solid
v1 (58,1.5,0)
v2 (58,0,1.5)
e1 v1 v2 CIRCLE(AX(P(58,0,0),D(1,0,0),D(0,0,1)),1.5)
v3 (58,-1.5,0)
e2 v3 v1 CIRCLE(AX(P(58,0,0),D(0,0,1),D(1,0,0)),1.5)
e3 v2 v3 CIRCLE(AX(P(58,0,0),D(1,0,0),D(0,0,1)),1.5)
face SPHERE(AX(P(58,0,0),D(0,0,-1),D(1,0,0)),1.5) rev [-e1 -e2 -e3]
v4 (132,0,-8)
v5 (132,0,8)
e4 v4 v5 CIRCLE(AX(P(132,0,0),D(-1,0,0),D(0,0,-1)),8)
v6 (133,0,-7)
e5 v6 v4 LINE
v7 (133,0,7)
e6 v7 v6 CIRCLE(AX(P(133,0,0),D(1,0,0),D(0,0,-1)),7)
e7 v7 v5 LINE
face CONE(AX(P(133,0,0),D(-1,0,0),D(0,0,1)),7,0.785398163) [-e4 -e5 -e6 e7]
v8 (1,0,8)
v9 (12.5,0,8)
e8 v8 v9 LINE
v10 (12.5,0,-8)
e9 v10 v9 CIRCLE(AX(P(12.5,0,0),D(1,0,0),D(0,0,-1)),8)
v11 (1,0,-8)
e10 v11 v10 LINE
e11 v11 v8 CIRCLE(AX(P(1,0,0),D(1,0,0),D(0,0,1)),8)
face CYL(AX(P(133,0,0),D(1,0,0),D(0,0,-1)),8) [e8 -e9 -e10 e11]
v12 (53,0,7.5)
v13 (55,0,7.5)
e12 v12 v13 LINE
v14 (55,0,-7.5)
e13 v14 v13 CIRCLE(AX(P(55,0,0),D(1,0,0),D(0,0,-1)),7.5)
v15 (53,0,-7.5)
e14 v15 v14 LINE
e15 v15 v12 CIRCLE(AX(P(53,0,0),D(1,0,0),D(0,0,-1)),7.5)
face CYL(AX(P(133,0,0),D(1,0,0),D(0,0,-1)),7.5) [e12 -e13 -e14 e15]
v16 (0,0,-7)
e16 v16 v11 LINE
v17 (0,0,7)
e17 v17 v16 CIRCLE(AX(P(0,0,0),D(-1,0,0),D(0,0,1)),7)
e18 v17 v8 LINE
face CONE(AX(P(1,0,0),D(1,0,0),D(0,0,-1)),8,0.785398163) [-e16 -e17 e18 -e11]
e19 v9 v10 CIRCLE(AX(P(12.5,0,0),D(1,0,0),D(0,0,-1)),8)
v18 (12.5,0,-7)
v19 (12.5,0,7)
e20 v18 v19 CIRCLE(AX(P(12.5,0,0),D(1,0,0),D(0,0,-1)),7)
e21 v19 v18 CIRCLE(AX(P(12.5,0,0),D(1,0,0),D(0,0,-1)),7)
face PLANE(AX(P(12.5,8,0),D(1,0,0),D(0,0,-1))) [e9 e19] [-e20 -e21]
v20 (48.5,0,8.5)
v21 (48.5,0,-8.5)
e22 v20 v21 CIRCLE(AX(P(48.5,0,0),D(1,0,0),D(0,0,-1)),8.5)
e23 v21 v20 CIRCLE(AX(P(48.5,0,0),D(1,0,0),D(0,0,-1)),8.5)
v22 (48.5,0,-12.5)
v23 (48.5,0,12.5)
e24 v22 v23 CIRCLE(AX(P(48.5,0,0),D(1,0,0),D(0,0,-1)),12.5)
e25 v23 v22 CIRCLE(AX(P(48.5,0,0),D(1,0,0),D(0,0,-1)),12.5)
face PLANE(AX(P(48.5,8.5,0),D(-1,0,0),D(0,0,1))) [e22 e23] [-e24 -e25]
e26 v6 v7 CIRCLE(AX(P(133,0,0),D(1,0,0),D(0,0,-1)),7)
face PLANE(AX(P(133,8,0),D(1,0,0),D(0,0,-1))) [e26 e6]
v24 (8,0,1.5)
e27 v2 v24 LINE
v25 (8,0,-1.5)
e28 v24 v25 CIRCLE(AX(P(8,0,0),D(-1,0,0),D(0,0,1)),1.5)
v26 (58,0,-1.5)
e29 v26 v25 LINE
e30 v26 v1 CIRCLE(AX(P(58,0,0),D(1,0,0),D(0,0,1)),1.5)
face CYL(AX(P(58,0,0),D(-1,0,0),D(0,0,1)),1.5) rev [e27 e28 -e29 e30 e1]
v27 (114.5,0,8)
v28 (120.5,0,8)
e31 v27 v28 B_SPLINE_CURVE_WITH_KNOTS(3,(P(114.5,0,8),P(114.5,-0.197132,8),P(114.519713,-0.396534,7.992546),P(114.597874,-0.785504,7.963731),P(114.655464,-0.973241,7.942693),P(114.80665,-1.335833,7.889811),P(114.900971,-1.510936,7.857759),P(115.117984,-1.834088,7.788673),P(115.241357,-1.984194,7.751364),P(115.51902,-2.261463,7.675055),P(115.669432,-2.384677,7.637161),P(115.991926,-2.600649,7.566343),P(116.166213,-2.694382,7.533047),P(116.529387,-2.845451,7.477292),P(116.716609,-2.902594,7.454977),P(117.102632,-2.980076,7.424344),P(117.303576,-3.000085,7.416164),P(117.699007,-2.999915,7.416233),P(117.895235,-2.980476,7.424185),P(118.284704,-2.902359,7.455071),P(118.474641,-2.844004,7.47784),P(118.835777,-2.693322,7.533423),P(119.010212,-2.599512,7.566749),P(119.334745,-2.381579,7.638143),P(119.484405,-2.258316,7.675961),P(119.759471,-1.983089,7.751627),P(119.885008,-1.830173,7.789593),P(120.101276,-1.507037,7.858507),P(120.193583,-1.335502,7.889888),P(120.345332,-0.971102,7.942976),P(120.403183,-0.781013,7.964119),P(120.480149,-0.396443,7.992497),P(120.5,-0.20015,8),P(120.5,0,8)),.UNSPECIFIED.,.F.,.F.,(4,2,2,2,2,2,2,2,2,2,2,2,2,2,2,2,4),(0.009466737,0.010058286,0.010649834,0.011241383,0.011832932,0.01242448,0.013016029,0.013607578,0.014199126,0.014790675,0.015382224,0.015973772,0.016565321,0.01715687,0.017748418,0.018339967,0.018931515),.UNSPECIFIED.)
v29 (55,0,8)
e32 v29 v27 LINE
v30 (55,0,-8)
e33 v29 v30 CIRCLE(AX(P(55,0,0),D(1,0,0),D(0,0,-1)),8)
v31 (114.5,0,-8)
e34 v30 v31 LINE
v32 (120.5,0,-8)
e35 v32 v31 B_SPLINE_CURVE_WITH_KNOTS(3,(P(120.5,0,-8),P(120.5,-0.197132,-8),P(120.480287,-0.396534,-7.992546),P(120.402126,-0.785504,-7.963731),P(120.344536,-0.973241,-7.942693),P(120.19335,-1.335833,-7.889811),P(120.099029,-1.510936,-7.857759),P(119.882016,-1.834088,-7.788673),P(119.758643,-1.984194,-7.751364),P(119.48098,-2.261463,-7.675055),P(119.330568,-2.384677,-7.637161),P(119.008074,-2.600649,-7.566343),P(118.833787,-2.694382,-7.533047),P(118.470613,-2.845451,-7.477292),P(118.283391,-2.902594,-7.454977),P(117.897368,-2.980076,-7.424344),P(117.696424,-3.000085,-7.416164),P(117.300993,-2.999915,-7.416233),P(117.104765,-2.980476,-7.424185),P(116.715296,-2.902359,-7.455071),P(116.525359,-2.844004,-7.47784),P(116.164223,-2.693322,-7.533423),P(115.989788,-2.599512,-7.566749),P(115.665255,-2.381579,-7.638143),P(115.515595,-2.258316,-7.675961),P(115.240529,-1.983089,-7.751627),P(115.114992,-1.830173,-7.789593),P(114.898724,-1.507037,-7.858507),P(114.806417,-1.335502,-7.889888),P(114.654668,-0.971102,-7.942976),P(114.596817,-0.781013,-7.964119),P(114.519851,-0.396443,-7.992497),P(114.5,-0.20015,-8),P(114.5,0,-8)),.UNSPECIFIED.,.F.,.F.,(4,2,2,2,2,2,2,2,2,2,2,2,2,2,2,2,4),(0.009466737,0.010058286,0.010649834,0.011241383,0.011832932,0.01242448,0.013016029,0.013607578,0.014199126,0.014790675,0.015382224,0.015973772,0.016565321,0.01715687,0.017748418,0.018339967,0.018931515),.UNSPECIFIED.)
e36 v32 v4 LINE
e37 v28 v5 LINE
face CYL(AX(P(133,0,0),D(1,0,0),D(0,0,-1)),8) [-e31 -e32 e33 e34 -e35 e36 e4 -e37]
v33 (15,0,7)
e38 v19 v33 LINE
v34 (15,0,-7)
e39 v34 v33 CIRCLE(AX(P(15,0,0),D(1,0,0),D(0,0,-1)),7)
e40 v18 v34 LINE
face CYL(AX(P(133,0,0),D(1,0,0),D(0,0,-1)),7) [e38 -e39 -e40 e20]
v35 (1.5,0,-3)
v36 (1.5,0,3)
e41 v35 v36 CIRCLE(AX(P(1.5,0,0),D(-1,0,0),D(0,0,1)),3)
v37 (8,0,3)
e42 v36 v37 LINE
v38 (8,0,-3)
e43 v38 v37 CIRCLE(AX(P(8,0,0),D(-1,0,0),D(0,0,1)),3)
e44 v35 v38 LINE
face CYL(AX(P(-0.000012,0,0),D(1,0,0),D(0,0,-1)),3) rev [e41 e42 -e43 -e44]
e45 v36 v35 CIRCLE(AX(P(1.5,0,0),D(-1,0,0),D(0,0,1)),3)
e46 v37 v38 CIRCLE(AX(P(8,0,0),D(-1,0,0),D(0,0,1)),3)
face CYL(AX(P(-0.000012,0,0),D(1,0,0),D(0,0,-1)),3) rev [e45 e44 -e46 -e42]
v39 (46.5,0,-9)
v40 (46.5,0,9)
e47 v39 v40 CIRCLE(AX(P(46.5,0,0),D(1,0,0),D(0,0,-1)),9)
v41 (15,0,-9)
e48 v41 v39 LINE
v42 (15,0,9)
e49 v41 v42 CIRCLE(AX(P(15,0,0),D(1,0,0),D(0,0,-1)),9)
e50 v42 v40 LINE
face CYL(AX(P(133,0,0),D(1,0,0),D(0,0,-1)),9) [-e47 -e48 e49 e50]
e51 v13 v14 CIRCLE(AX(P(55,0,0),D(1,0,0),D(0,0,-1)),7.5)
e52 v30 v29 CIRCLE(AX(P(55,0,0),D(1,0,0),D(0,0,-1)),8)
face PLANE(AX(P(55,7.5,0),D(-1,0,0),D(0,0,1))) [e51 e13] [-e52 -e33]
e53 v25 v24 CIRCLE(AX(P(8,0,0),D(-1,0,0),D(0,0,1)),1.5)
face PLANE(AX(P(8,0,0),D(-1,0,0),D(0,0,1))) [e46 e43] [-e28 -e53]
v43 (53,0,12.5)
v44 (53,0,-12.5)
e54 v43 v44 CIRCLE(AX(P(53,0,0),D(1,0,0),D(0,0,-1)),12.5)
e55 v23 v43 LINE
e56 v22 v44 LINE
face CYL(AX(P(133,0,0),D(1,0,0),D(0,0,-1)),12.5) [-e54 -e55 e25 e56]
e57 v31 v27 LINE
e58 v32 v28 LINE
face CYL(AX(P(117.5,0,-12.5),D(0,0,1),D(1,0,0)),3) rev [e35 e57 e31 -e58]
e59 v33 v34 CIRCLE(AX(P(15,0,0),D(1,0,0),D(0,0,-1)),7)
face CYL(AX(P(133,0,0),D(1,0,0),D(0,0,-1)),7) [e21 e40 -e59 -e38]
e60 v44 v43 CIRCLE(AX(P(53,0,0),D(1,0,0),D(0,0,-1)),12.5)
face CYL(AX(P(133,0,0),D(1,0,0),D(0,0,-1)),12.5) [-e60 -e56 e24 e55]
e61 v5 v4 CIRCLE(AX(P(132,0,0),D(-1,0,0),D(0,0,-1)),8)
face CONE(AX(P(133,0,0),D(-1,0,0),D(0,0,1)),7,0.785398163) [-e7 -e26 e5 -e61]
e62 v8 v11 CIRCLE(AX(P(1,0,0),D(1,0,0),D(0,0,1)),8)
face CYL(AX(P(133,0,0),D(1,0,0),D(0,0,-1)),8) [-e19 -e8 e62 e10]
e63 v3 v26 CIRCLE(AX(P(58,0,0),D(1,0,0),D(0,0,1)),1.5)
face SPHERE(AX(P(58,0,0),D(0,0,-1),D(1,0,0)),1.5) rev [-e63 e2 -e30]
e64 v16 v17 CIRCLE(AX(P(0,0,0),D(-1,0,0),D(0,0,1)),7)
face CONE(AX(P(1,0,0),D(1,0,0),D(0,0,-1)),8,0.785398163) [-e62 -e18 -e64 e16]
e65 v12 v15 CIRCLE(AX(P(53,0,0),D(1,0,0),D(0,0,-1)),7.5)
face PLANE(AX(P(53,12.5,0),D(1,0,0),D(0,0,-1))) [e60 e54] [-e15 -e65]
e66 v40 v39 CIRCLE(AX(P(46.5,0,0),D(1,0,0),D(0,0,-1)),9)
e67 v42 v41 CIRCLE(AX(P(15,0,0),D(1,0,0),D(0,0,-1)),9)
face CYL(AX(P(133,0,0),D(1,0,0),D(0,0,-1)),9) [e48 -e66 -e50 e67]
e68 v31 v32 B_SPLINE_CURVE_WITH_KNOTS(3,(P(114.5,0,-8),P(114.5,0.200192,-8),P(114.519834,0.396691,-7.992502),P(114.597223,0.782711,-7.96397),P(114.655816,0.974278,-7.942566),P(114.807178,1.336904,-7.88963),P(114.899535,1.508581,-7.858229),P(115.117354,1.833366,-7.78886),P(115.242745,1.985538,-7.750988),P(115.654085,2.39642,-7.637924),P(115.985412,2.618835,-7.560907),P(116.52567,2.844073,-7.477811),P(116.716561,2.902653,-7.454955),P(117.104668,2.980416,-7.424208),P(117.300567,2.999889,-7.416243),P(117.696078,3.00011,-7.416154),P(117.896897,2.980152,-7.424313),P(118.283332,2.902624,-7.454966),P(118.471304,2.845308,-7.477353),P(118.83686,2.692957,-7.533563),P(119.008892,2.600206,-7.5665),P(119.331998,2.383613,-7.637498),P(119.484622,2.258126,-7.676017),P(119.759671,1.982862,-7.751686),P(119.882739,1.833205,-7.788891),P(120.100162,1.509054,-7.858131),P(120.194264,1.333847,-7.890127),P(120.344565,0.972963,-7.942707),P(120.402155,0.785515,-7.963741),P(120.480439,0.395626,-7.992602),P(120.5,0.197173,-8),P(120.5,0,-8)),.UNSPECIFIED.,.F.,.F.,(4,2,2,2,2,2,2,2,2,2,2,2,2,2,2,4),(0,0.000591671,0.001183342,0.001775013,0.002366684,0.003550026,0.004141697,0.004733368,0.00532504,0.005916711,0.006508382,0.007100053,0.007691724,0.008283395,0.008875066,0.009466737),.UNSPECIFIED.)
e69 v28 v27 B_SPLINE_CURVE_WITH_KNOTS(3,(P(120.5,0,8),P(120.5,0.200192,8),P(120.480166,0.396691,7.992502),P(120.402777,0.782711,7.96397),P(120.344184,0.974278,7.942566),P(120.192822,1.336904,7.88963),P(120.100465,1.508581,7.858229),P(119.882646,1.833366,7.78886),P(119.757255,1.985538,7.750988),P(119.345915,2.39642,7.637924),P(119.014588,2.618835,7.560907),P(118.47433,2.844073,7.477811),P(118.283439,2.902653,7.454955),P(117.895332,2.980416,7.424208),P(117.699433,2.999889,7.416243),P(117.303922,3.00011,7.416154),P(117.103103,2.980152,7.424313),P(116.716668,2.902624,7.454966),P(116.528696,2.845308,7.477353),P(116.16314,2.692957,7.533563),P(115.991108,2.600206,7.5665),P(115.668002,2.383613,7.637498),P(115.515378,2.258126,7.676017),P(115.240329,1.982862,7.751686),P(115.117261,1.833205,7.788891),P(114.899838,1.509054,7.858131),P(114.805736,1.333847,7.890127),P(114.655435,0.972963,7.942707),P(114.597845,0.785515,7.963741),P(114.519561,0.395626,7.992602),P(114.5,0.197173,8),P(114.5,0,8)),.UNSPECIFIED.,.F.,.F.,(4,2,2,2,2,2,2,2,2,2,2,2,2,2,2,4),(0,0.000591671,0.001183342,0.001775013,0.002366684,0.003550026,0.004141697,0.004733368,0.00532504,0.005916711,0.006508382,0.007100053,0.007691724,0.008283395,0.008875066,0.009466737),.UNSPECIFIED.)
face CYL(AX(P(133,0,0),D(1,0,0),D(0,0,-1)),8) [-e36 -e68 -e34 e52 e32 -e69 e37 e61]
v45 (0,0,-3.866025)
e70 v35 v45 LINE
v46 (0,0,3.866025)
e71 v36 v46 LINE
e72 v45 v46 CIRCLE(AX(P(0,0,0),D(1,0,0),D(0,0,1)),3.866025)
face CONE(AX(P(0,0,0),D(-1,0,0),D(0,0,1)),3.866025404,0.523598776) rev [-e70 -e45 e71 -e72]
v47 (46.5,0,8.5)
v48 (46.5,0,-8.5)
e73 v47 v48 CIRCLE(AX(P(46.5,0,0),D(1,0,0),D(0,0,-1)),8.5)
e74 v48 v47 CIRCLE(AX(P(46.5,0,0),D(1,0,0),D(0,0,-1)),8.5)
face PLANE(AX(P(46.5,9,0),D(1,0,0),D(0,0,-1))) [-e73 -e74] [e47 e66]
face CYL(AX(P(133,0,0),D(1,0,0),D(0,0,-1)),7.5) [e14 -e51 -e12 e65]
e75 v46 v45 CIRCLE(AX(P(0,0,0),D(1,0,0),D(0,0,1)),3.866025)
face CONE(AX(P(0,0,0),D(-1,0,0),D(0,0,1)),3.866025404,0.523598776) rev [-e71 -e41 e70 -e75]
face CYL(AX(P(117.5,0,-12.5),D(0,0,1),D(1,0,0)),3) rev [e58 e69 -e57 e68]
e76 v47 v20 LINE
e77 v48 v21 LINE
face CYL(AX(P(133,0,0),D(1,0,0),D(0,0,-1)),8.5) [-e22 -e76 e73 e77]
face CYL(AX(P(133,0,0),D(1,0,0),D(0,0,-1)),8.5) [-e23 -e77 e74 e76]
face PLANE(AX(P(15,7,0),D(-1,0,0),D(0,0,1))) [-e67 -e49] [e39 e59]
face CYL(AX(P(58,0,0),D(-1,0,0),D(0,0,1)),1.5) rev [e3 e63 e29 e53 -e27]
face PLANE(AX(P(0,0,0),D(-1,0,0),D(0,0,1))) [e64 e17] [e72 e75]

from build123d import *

# Parameters (mm, degrees)
CUT_EXTRUDE1_DEPTH      = 135.169668703
CUT_EXTRUDE1_DEPTH_BACK = 135.169668703
SKETCH2_R               = 3
CUT_EXTRUDE2_DEPTH      = 135.169668803
CUT_EXTRUDE2_DEPTH_BACK = 8
SKETCH3_R               = 3
SKETCH4_R               = 1.5
CUT_EXTRUDE3_DEPTH      = 50
CHAMFER1_SIZE           = 1.5
CHAMFER1_SIZE2          = 0.866025404
CHAMFER2_SIZE           = 1


with BuildPart() as part:
    # Sketch1 → Revolve1 (revolve)
    with BuildSketch(Plane.XY, mode=Mode.PRIVATE) as revolve1_sk:
        Polygon((0, 0), (0, 8), (12.5, 8), (12.5, 7), (15, 7), (15, 9), (46.5, 9), (46.5, 8.5), (48.5, 8.5), (48.5, 12.5), (53, 12.5), (53, 7.5), (55, 7.5), (55, 8), (133, 8), (133, 0), align=None)
    revolve(revolve1_sk.sketch.rotate(Axis((133, 0, 0), (-1, 0, 0)), 90), axis=Axis((133, 0, 0), (-1, 0, 0)))

    # Sketch2 → Cut-Extrude1 (cut, two sides: drawn at the far end of the back side and taken through both)
    with BuildSketch(Plane.XY.offset(-CUT_EXTRUDE1_DEPTH_BACK)):
        with Locations((117.5, 0)):
            Circle(SKETCH2_R)
    extrude(amount=CUT_EXTRUDE1_DEPTH + CUT_EXTRUDE1_DEPTH_BACK, mode=Mode.SUBTRACT)

    # Sketch3 → Cut-Extrude2 (cut, two sides: drawn at the far end of the back side and taken through both)
    with BuildSketch(Plane.ZY.offset(-CUT_EXTRUDE2_DEPTH_BACK)):
        with Locations(Location((0, 0, 0), (0, 0, 180))):
            Circle(SKETCH3_R)
    extrude(amount=CUT_EXTRUDE2_DEPTH + CUT_EXTRUDE2_DEPTH_BACK, mode=Mode.SUBTRACT)

    # Sketch4 → Cut-Extrude3 (cut)
    with BuildSketch(Plane.ZY.offset(-8)):
        Circle(SKETCH4_R)
    extrude(amount=-CUT_EXTRUDE3_DEPTH, mode=Mode.SUBTRACT)

    # Chamfer1
    chamfer1_edges = [part.edges().sort_by_distance(p)[0] for p in [
        (0, 0, 3),
    ]]
    chamfer1_side = [part.faces().sort_by_distance(p)[0] for p in [
        (4, 0, 3),
    ]]
    chamfer(chamfer1_edges, length=CHAMFER1_SIZE, length2=CHAMFER1_SIZE2, reference=chamfer1_side[0])

    # Chamfer2
    chamfer2_edges = [part.edges().sort_by_distance(p)[0] for p in [
        (133, 0, 8),
        (0, 0, 8),
    ]]
    chamfer(chamfer2_edges, length=CHAMFER2_SIZE)

    # Sketch5 → Cut-Revolve1 (revolve, cut)
    with BuildSketch(Plane.XY):
        with BuildLine():
            Line((58, 1.5), (58, -1.5))
            ThreePointArc((58, -1.5), (59.5, 0), (58, 1.5))
        make_face()
    revolve(axis=Axis((58, 1.5, 0), (0, -1, 0)), mode=Mode.SUBTRACT)


solid = part.part
